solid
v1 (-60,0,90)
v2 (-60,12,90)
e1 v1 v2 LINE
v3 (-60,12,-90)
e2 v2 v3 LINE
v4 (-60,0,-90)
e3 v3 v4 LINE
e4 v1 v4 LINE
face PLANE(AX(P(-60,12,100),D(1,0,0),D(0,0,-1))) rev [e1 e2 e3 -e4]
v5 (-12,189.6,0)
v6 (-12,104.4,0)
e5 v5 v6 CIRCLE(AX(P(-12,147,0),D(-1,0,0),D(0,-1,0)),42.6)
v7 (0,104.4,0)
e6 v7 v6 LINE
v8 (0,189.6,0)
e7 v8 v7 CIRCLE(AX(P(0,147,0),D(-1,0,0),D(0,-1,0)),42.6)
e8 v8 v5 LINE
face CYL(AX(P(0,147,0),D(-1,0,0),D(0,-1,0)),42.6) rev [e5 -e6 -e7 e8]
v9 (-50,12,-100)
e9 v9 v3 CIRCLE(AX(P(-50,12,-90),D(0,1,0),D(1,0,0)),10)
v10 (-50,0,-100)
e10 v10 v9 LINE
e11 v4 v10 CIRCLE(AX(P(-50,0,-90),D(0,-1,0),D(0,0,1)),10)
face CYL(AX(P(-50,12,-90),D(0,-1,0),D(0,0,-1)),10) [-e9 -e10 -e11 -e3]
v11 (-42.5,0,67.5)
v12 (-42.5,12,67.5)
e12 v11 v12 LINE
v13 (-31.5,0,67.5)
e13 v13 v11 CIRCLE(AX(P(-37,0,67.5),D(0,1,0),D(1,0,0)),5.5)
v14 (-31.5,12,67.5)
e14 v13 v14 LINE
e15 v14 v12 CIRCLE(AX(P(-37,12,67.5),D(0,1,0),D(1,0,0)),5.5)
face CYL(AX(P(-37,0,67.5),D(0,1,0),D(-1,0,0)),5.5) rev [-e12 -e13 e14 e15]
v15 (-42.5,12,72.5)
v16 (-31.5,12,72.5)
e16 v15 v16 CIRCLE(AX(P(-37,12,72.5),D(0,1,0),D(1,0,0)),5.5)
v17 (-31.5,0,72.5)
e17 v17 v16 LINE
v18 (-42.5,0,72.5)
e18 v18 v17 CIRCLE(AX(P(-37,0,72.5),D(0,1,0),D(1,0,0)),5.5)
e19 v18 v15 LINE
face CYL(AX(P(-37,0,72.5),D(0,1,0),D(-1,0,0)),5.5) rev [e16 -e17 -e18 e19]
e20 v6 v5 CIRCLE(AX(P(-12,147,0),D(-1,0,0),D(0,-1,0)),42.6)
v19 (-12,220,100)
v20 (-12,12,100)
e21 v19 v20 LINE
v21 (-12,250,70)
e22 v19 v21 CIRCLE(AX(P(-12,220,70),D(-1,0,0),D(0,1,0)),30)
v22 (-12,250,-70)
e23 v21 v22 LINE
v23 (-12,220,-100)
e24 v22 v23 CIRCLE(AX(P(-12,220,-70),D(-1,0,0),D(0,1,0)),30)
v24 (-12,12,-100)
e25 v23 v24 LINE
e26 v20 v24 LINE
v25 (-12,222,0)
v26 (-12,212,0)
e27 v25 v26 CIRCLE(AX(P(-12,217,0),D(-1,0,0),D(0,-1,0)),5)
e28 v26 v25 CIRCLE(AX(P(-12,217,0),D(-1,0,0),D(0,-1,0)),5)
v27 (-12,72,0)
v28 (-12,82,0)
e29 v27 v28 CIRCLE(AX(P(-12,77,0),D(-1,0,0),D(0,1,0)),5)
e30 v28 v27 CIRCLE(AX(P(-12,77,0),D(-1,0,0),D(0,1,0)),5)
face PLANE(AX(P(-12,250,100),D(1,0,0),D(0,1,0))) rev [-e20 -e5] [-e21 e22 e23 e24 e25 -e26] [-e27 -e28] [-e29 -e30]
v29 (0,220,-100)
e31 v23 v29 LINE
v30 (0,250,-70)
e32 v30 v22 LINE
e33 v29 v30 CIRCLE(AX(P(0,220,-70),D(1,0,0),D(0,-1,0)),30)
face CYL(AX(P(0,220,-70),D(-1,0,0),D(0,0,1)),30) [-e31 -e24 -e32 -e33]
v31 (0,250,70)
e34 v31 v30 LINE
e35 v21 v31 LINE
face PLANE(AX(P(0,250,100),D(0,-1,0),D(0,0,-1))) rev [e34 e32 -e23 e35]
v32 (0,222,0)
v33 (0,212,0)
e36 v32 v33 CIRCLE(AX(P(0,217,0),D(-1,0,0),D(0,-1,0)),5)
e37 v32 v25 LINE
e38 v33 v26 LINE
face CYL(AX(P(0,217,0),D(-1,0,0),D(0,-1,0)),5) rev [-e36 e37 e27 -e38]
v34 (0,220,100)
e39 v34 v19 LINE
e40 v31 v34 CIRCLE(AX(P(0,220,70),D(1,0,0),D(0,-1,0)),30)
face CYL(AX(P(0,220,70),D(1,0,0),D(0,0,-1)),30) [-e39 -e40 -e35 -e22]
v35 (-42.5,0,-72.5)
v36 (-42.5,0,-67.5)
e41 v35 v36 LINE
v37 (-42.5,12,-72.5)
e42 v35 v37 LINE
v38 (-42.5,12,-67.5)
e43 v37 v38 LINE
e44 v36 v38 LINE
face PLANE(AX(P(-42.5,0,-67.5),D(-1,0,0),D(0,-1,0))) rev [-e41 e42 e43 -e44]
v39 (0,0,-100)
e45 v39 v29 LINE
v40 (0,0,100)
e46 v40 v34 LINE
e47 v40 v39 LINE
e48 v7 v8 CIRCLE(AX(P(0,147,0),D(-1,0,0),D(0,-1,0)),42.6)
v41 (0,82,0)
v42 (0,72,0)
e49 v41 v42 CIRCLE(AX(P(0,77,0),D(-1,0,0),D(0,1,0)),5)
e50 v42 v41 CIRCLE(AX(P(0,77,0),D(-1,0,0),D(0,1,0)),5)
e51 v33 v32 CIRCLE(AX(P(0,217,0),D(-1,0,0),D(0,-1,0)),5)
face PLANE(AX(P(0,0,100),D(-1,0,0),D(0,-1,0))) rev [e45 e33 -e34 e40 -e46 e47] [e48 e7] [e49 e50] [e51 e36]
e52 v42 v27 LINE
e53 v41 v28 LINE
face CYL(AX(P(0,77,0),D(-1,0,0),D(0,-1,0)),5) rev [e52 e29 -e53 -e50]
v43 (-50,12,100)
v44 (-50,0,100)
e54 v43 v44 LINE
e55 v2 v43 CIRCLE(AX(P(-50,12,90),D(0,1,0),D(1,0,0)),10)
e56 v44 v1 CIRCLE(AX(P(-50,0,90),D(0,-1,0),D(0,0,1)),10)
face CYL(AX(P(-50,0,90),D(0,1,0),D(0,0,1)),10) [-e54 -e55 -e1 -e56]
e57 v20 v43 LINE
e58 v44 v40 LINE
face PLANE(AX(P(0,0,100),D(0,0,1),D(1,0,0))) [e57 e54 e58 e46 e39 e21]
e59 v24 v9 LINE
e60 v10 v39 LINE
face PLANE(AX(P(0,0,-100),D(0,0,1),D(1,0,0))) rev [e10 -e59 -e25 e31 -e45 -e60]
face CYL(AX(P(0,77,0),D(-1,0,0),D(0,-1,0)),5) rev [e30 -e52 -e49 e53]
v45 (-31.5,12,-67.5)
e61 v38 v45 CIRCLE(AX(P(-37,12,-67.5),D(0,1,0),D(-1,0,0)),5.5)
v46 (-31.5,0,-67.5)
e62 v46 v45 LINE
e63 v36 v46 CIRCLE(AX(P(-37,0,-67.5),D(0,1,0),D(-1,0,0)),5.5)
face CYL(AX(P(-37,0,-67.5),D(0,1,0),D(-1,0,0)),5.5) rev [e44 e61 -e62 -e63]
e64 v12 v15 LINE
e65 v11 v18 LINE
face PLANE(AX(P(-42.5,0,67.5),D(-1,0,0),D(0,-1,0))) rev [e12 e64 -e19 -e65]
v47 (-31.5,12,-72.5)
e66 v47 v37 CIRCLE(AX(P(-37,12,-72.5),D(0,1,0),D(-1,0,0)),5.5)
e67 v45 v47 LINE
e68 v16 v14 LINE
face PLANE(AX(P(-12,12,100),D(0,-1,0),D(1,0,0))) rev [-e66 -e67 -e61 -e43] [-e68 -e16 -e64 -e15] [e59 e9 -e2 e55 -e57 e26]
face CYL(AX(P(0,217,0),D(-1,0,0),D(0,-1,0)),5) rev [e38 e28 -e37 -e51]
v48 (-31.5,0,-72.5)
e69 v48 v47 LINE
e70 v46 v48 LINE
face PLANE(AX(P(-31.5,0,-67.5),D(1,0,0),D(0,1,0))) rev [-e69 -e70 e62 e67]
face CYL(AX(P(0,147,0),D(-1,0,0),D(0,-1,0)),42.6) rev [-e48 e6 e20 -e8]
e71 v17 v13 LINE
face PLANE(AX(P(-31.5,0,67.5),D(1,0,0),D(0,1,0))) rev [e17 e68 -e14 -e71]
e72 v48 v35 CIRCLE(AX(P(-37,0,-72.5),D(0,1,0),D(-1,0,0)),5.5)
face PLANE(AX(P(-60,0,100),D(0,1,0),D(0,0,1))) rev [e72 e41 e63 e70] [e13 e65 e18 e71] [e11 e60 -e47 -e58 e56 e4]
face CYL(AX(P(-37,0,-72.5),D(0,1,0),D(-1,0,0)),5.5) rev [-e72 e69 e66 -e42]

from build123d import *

# Parameters (mm, degrees)
BOSS_EXTRUDE_1_DEPTH = 100
CUT_EXTRUDE_1_DEPTH  = 266.035846632
SKETCH_3_R           = 42.6
SKETCH_3_R_2         = 5
CUT_EXTRUDE_2_DEPTH  = 274.50319925
FILLET_1_R           = 30
FILLET_2_R           = 10


with BuildPart() as part:
    # Sketch 1 → Boss-Extrude 1 (new, symmetric)
    with BuildSketch(Plane.XY):
        Polygon((-60, 0), (0, 0), (0, 250), (-12, 250), (-12, 12), (-60, 12), align=None)
    extrude(amount=BOSS_EXTRUDE_1_DEPTH, both=True)

    # Sketch 2 → Cut-Extrude 1 (cut, through all)
    with BuildSketch(Plane(origin=(0, 12, 0), x_dir=(1, 0, 0), z_dir=(0, 1, 0))):
        with BuildLine():
            Line((-42.5, 67.5), (-42.5, 72.5))
            ThreePointArc((-42.5, 72.5), (-37, 78), (-31.5, 72.5))
            Line((-31.5, 72.5), (-31.5, 67.5))
            ThreePointArc((-31.5, 67.5), (-37, 62), (-42.5, 67.5))
        make_face()
        with BuildLine():
            Line((-42.5, -67.5), (-42.5, -72.5))
            ThreePointArc((-42.5, -72.5), (-37, -78), (-31.5, -72.5))
            Line((-31.5, -72.5), (-31.5, -67.5))
            ThreePointArc((-31.5, -67.5), (-37, -62), (-42.5, -67.5))
        make_face()
    extrude(amount=-CUT_EXTRUDE_1_DEPTH, mode=Mode.SUBTRACT)

    # Sketch 3 → Cut-Extrude 2 (cut, through all)
    with BuildSketch(Plane.ZY.offset(12)):
        with Locations(Location((0, 147, 0), (0, 0, 270))):
            Circle(SKETCH_3_R)
        with Locations(Location((0, 217, 0), (0, 0, 270))):
            Circle(SKETCH_3_R_2)
        with Locations(Location((0, 77, 0), (0, 0, 90))):
            Circle(SKETCH_3_R_2)
    extrude(amount=-CUT_EXTRUDE_2_DEPTH, mode=Mode.SUBTRACT)

    # Fillet 1
    fillet_1_edges = [part.edges().sort_by_distance(p)[0] for p in [
        (-6, 250, 100),
        (-6, 250, -100),
    ]]
    fillet(fillet_1_edges, radius=FILLET_1_R)

    # Fillet 2
    fillet_2_edges = [part.edges().sort_by_distance(p)[0] for p in [
        (-60, 6, 100),
        (-60, 6, -100),
    ]]
    fillet(fillet_2_edges, radius=FILLET_2_R)


solid = part.part
